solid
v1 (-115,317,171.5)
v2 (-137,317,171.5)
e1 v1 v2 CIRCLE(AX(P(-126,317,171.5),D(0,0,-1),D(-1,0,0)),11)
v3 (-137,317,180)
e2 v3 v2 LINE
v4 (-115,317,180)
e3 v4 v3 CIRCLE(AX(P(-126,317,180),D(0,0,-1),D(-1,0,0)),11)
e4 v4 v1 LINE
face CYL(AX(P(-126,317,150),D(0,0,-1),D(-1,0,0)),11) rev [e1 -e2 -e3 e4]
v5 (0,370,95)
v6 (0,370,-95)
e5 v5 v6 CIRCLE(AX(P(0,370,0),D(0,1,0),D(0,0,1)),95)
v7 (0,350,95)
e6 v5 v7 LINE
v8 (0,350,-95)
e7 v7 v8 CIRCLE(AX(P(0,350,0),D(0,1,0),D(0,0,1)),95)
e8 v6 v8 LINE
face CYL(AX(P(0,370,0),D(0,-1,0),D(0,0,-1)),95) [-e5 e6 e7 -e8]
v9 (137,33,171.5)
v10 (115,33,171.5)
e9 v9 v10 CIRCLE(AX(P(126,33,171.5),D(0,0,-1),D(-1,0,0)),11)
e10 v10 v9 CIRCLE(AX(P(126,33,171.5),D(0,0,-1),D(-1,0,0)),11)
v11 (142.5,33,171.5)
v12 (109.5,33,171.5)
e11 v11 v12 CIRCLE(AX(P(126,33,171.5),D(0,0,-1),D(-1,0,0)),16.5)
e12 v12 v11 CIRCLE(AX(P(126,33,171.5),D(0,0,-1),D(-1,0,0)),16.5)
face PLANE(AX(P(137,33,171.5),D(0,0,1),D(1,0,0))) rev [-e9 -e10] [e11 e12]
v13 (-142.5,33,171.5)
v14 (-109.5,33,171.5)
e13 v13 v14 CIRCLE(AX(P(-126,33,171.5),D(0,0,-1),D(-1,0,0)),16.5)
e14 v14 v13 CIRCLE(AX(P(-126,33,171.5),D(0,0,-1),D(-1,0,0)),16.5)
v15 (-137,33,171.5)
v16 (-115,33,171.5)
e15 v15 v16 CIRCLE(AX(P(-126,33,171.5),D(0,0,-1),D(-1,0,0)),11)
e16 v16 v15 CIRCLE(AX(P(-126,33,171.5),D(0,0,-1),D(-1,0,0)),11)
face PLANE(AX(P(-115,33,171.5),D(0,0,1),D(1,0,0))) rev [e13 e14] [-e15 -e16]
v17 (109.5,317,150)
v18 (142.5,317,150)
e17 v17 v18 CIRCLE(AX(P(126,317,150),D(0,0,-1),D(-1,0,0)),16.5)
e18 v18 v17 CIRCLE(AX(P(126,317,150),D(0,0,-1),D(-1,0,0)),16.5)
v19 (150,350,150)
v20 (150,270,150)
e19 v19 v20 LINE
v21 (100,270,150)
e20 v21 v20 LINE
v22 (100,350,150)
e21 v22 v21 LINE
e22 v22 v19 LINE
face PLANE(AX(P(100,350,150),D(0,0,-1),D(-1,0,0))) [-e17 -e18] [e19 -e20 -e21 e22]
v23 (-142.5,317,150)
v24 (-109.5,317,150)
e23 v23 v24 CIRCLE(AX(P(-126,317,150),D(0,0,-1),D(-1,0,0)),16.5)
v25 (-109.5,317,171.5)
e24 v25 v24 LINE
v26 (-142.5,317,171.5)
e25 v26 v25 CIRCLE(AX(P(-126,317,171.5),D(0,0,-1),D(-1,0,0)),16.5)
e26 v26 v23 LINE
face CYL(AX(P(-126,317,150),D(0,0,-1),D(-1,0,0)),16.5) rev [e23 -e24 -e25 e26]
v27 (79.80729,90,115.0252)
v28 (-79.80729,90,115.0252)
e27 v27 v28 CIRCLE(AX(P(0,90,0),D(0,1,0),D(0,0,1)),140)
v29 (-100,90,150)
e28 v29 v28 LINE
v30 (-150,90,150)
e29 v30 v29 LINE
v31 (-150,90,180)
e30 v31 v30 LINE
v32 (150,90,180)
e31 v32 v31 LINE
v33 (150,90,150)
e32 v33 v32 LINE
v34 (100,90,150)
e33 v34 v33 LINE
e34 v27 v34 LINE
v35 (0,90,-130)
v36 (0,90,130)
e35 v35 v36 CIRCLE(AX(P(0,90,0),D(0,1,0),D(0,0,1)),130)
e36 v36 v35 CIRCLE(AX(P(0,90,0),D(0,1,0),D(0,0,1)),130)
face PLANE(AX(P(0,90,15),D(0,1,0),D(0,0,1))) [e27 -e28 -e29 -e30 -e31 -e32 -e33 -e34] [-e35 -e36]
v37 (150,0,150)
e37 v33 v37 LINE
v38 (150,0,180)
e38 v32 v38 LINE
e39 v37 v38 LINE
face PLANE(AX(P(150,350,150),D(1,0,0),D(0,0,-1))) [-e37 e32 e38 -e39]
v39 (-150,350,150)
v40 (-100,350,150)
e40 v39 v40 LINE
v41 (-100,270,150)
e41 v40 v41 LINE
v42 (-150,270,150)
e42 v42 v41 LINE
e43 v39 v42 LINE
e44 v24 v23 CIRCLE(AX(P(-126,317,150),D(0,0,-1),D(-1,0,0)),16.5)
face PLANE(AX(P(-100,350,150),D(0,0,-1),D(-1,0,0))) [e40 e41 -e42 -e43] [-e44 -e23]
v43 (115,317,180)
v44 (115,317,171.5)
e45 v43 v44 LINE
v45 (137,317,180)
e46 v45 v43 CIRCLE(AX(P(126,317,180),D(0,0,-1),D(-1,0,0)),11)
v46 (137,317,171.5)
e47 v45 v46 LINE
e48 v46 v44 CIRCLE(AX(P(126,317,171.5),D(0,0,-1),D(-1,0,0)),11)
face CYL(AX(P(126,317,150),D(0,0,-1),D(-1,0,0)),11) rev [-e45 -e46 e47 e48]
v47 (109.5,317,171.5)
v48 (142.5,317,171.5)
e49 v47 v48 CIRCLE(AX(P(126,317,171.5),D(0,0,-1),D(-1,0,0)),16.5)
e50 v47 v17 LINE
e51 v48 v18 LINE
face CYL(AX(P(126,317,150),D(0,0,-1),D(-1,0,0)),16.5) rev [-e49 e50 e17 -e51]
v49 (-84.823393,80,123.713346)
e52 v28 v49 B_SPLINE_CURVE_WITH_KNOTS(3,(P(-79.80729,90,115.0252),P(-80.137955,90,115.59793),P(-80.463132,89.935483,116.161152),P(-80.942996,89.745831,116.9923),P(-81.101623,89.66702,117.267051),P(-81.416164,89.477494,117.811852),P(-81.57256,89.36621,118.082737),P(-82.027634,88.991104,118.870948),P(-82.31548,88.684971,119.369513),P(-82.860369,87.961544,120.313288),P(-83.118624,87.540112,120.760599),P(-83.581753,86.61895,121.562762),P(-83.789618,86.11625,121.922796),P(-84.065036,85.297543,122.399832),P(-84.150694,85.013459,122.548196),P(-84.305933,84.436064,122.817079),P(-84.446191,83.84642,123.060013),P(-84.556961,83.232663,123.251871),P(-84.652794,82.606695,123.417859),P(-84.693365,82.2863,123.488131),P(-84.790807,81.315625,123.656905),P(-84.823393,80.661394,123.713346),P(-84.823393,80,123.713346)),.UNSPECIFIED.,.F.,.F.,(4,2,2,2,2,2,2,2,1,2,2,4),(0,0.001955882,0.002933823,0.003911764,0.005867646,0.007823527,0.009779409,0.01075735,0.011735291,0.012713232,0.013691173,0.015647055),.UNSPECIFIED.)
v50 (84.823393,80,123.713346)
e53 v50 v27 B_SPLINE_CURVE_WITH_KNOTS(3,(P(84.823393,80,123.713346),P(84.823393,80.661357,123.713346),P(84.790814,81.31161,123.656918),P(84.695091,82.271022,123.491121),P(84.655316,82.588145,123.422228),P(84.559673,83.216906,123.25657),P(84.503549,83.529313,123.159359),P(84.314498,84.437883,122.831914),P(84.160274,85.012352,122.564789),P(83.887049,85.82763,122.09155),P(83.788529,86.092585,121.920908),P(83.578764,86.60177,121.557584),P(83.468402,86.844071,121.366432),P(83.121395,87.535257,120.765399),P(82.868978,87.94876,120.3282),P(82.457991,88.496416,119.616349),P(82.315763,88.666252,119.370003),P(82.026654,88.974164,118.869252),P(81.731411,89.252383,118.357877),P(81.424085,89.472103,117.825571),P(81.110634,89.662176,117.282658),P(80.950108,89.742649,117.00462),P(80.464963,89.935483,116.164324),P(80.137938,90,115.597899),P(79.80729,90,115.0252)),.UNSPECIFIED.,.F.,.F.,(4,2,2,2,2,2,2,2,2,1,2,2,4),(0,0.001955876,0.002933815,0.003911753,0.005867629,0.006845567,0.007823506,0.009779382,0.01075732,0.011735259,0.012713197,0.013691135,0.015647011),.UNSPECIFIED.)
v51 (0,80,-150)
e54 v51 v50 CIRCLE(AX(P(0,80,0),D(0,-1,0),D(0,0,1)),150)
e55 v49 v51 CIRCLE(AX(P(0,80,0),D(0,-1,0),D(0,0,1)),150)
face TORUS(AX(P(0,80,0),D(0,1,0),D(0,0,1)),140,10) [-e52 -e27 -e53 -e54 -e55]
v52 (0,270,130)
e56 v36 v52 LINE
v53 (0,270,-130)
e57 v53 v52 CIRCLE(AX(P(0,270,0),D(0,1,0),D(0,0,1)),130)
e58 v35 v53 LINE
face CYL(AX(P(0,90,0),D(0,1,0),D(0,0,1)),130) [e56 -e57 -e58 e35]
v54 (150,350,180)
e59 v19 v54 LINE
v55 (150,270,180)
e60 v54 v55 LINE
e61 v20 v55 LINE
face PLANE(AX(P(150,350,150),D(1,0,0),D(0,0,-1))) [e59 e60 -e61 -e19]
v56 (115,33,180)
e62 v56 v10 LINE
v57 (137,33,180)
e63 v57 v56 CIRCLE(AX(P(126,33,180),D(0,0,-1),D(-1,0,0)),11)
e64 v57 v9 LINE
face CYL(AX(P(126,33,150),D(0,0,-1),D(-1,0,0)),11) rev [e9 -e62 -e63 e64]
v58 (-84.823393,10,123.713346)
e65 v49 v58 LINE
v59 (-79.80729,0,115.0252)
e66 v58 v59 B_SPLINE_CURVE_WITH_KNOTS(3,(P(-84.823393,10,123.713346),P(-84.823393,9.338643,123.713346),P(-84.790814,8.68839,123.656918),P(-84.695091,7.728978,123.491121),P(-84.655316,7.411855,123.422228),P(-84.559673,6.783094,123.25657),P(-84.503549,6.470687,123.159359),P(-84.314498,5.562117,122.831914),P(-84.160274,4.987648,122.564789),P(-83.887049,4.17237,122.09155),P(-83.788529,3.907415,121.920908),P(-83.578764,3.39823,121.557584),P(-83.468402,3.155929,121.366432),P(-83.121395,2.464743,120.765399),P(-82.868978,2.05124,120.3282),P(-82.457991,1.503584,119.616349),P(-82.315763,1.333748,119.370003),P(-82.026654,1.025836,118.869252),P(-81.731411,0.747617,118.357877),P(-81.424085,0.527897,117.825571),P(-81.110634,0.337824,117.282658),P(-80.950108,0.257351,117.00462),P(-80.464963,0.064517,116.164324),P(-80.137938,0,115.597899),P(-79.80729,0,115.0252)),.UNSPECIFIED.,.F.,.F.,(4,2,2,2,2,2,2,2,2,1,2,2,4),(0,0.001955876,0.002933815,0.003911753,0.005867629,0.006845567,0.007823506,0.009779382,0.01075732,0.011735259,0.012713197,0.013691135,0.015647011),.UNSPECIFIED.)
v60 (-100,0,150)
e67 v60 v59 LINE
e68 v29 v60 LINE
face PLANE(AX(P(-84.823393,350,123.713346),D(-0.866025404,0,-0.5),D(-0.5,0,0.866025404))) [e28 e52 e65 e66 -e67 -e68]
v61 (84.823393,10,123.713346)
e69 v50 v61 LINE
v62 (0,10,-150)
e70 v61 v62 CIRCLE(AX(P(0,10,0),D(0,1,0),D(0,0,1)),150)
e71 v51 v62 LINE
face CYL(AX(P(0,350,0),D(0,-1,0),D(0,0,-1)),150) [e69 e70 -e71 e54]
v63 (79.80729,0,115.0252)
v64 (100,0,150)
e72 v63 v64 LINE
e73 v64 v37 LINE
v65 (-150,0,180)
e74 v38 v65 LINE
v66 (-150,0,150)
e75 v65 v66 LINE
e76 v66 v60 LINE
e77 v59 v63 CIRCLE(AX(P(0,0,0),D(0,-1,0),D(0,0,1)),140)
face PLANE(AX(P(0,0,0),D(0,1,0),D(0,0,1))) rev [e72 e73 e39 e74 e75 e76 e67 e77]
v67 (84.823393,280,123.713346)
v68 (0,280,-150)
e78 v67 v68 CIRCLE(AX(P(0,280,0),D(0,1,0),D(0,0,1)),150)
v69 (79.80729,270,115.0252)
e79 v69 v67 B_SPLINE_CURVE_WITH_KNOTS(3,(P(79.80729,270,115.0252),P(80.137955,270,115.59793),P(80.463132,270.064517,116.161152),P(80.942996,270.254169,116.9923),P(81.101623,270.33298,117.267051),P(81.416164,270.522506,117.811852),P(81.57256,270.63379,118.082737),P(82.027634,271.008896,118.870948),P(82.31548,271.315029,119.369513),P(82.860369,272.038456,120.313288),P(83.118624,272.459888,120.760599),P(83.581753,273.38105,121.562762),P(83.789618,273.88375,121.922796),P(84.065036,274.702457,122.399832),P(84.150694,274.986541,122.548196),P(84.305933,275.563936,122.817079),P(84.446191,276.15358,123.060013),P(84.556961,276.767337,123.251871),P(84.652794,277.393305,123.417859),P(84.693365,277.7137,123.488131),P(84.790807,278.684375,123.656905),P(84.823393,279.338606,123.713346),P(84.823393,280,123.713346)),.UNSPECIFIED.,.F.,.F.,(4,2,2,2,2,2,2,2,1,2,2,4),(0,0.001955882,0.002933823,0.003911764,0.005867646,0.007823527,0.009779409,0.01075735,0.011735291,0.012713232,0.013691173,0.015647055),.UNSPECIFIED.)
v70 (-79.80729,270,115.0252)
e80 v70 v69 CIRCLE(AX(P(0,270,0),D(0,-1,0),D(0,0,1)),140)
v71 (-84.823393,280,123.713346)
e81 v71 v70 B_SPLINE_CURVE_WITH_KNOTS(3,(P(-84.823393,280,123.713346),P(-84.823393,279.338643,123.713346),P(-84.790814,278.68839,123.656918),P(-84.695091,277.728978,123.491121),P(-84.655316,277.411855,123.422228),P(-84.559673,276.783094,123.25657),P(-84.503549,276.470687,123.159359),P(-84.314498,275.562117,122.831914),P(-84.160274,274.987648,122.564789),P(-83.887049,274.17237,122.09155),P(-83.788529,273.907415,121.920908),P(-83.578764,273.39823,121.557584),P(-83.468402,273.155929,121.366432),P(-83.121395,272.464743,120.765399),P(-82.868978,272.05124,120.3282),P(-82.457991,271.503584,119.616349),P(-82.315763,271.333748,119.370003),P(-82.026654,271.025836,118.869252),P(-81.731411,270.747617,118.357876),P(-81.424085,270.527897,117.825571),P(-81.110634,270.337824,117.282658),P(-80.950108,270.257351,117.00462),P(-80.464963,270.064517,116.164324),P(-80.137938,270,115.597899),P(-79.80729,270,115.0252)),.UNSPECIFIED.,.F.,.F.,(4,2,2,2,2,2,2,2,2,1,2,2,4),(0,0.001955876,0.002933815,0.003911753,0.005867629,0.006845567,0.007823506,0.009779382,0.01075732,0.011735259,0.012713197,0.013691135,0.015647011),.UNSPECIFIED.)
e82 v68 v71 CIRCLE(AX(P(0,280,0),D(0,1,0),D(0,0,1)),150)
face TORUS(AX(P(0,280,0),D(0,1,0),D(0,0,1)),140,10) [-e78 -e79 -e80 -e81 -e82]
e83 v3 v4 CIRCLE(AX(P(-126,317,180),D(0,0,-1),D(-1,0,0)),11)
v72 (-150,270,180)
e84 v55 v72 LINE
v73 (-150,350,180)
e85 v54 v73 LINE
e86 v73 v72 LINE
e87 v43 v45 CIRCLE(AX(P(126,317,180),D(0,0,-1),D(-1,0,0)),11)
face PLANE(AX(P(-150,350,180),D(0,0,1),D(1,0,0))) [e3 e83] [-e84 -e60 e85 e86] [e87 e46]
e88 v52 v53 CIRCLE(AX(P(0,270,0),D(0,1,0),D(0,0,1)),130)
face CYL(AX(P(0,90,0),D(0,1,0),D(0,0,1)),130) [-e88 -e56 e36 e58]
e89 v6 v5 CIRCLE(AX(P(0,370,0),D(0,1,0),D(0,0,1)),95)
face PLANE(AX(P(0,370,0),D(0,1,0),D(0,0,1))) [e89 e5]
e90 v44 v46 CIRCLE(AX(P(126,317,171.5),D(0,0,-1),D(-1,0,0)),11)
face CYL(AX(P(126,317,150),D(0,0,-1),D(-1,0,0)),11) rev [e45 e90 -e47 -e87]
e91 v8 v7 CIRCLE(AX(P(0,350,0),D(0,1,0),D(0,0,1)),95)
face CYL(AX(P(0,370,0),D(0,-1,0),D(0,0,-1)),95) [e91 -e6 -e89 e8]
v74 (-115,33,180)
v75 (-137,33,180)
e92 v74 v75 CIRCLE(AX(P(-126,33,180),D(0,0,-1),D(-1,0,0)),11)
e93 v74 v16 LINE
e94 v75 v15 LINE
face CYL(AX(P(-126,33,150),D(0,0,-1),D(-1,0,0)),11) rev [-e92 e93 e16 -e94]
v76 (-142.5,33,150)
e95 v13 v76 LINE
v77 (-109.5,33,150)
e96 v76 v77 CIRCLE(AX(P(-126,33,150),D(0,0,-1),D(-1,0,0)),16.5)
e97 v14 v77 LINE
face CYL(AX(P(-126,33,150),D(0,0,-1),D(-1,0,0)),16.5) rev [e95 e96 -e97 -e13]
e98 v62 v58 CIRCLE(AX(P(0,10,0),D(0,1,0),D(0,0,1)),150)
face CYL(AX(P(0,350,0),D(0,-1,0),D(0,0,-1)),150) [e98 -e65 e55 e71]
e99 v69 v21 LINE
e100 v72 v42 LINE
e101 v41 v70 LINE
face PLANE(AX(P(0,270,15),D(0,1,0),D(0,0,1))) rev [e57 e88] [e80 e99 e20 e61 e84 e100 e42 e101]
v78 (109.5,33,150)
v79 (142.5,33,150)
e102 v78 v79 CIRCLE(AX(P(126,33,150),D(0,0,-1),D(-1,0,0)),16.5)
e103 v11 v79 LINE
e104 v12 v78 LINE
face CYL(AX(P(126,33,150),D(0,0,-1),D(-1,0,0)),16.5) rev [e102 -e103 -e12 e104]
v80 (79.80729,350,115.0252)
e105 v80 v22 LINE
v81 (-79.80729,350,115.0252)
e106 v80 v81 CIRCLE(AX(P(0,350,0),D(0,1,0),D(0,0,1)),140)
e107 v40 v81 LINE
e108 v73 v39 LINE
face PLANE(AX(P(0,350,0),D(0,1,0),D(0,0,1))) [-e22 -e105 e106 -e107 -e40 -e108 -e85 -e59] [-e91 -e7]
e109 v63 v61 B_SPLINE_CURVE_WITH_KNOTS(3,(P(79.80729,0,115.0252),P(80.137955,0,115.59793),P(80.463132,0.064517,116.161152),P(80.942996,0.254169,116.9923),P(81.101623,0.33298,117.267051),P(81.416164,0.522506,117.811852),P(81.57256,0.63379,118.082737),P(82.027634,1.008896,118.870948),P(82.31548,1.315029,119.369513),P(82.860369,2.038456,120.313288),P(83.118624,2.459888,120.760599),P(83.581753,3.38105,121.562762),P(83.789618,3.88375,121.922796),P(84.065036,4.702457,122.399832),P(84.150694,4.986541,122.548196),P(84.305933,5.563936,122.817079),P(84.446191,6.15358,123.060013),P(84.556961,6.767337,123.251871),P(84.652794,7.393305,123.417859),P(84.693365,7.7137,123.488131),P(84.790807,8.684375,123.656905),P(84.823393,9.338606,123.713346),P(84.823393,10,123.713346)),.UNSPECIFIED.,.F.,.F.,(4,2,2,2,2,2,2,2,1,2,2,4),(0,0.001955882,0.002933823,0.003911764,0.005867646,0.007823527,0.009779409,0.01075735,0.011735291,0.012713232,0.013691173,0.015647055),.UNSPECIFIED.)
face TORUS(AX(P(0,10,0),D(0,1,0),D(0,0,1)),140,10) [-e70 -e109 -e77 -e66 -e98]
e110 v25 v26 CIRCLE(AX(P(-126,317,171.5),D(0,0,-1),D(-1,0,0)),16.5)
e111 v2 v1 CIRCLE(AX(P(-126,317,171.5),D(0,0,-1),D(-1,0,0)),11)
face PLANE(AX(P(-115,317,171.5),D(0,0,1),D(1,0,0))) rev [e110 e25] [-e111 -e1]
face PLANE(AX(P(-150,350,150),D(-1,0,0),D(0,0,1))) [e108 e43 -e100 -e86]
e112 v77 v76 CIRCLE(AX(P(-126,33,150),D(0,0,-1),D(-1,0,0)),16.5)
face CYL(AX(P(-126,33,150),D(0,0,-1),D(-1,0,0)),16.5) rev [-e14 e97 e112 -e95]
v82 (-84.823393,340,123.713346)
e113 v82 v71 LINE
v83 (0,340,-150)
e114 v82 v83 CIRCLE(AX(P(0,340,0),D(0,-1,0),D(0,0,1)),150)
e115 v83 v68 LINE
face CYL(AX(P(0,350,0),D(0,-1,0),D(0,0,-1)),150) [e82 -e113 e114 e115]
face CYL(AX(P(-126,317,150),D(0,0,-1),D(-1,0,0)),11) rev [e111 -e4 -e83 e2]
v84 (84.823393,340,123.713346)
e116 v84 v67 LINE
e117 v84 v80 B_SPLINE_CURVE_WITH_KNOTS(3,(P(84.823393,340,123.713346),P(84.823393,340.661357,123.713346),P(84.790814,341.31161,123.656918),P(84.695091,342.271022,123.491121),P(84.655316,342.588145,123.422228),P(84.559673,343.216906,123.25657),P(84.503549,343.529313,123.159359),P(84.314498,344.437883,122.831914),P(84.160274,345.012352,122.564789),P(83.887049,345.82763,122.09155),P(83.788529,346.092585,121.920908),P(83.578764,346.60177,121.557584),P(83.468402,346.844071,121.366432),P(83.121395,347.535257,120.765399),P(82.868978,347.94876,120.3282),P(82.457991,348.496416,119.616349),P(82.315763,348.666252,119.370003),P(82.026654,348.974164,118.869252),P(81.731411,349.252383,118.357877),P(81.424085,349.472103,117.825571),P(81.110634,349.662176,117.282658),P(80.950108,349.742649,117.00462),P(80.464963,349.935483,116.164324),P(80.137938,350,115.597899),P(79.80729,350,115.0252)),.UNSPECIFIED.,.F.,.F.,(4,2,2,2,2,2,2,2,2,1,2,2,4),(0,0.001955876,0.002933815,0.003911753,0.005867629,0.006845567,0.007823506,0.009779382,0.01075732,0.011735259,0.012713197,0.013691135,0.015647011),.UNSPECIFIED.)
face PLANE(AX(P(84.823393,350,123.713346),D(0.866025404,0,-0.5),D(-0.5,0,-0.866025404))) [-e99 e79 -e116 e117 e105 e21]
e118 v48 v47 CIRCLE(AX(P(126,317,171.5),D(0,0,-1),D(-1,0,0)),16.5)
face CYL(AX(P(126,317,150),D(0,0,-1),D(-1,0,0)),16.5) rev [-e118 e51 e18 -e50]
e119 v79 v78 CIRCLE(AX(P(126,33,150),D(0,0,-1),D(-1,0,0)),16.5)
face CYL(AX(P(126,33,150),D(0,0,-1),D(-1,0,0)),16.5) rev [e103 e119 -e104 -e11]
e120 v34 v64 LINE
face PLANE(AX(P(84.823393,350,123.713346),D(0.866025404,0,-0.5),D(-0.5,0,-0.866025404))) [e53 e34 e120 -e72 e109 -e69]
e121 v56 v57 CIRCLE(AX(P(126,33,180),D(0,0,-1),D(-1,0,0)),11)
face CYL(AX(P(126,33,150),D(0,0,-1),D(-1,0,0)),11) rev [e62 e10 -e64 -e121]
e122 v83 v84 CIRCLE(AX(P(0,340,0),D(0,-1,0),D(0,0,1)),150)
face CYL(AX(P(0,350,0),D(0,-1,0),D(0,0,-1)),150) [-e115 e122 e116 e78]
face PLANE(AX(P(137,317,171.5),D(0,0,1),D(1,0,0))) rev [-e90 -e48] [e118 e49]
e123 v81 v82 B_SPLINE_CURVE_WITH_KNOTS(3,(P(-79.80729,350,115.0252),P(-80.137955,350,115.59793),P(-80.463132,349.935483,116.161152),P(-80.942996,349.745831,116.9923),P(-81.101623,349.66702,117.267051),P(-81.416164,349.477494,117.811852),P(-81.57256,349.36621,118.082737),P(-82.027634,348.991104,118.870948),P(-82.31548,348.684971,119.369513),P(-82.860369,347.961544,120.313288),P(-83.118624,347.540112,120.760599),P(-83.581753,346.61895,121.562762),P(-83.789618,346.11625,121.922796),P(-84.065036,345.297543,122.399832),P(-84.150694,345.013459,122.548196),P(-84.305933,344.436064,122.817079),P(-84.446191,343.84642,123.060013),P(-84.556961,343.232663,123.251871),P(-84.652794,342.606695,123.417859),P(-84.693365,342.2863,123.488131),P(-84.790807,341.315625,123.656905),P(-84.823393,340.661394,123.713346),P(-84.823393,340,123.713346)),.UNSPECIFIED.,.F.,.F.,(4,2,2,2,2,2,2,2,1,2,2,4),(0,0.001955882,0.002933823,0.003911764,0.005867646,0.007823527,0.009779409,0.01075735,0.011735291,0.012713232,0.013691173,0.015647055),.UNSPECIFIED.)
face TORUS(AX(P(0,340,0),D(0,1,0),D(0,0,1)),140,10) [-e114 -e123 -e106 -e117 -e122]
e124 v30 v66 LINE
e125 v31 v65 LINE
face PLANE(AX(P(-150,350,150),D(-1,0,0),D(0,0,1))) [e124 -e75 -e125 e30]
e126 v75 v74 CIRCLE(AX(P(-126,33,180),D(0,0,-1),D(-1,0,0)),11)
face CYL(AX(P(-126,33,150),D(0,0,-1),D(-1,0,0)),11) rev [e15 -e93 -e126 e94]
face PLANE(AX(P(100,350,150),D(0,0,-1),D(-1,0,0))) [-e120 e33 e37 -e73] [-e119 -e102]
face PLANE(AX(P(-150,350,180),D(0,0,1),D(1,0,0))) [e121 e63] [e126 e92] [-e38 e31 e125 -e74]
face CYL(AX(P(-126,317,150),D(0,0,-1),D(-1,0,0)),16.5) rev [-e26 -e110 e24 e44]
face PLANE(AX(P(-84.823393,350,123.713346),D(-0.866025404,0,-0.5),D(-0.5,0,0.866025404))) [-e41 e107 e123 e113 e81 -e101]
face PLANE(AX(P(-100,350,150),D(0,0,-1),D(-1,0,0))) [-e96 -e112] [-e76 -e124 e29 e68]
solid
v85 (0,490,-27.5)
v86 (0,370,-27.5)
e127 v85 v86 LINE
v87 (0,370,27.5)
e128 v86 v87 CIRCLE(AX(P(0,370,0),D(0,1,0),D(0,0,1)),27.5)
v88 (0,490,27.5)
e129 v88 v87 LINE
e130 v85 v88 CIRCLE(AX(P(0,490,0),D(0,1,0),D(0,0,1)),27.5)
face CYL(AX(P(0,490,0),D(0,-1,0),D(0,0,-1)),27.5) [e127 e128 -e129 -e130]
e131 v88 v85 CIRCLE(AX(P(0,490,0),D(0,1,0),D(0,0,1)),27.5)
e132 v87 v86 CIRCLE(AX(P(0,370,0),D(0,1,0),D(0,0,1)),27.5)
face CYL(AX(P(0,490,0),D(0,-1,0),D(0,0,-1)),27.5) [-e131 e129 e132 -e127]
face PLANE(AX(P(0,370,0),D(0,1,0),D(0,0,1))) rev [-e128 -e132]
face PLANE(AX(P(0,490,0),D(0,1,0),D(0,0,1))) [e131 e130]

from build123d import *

# Parameters (mm, degrees)
SKETCH_1_R               = 150
EXTRUDE_1_DEPTH          = 350
EXTRUDE_2_DEPTH          = 350
SKETCH_3_R               = 95
EXTRUDE_3_DEPTH          = 20
CUT_EXTRUDE_START        = -80
SKETCH_4_OUTSIDE_W       = 417.896
SKETCH_4_OUTSIDE_H       = 447.896
SKETCH_4_OUTSIDE_R       = 130
CUT_EXTRUDE_1_DEPTH      = 180
FILLET_1_R               = 10
SKETCH_5_R               = 27.5
EXTRUDE_4_DEPTH          = 120
HOLE_WIZARD_1_AT_2_COUNT = 2
HOLE_WIZARD_1_AT_2_PITCH = 284
HOLE_WIZARD_1_AT_3_COUNT = 2
HOLE_WIZARD_1_AT_3_PITCH = 379.684079203
HOLE_WIZARD_1_AT_4_COUNT = 2
HOLE_WIZARD_1_AT_4_PITCH = 252


with BuildPart() as part:
    # 草图1 → 凸台-拉伸1 (new body)
    with BuildSketch(Plane(origin=(0, 0, 0), x_dir=(1, 0, 0), z_dir=(0, 1, 0))):
        with Locations(Location((0, 0, 0), (0, 0, 270))):
            Circle(SKETCH_1_R)
    extrude(amount=EXTRUDE_1_DEPTH)

    # 草图2 → 凸台-拉伸2 (add)
    with BuildSketch(Plane.XZ):
        with BuildLine():
            Line((-84.823393206, 123.713345946), (-100, 150))
            Line((-100, 150), (-150, 150))
            Line((-150, 150), (-150, 180))
            Line((-150, 180), (150, 180))
            Line((150, 180), (150, 150))
            Line((150, 150), (100, 150))
            Line((100, 150), (84.823393206, 123.713345946))
            ThreePointArc((84.823393206, 123.713345946), (0, 150), (-84.823393206, 123.713345946))
        make_face()
    extrude(amount=-EXTRUDE_2_DEPTH)

    # 草图3 → 凸台-拉伸3 (add)
    with BuildSketch(Plane(origin=(0, 350, 0), x_dir=(1, 0, 0), z_dir=(0, 1, 0))):
        with Locations(Location((0, 0, 0), (0, 0, 270))):
            Circle(SKETCH_3_R)
    extrude(amount=EXTRUDE_3_DEPTH)

    # 草图4 outside → 切除-拉伸1 (cut)
    with BuildSketch(Plane(origin=(0, 350, 0), x_dir=(1, 0, 0), z_dir=(0, 1, 0)).offset(CUT_EXTRUDE_START)):
        with Locations((0, -15)):
            Rectangle(SKETCH_4_OUTSIDE_W, SKETCH_4_OUTSIDE_H)
        with Locations(Location((0, 0, 0), (0, 0, 270))):
            Circle(SKETCH_4_OUTSIDE_R, mode=Mode.SUBTRACT)
    extrude(amount=-CUT_EXTRUDE_1_DEPTH, mode=Mode.SUBTRACT)

    # 圆角1
    fillet_1_edges = [part.edges().sort_by_distance(p)[0] for p in [
        (0, 0, -150),
        (0, 350, -150),
        (0, 270, -150),
        (0, 90, -150),
    ]]
    fillet(fillet_1_edges, radius=FILLET_1_R)

    # 草图7 → 打孔尺寸(%根据)内六角圆柱头螺钉的类型1 (revolve, cut)
    with BuildSketch(Plane(origin=(126, 317, 150), x_dir=(0, 1, 0), z_dir=(1, 0, 0))):
        Polygon((0, 0), (0, 30), (11, 30), (11, 21.5), (16.5, 21.5), (16.5, 0), align=None)
    hole_wizard_1 = revolve(axis=Axis((126, 317, 143.65), (0, 0, 1)), mode=Mode.SUBTRACT)

    # 打孔尺寸(%根据)内六角圆柱头螺钉的类型1 at 2: 打孔尺寸(%根据)内六角圆柱头螺钉的类型1 ×2
    with Locations(*[(0, -i * HOLE_WIZARD_1_AT_2_PITCH, 0) for i in range(1, HOLE_WIZARD_1_AT_2_COUNT)]):
        add(hole_wizard_1, mode=Mode.SUBTRACT)

    # 打孔尺寸(%根据)内六角圆柱头螺钉的类型1 at 3: 打孔尺寸(%根据)内六角圆柱头螺钉的类型1 ×2
    with Locations(*[Vector(-0.6637096834009412, -0.747990278118521, 0) * (i * HOLE_WIZARD_1_AT_3_PITCH) for i in range(1, HOLE_WIZARD_1_AT_3_COUNT)]):
        add(hole_wizard_1, mode=Mode.SUBTRACT)

    # 打孔尺寸(%根据)内六角圆柱头螺钉的类型1 at 4: 打孔尺寸(%根据)内六角圆柱头螺钉的类型1 ×2
    with Locations(*[(-i * HOLE_WIZARD_1_AT_4_PITCH, 0, 0) for i in range(1, HOLE_WIZARD_1_AT_4_COUNT)]):
        add(hole_wizard_1, mode=Mode.SUBTRACT)


with BuildPart() as body_2:
    # 草图5 → 凸台-拉伸4 (new body)
    with BuildSketch(Plane(origin=(0, 370, 0), x_dir=(1, 0, 0), z_dir=(0, 1, 0))):
        with Locations(Location((0, 0, 0), (0, 0, 90))):
            Circle(SKETCH_5_R)
    extrude(amount=EXTRUDE_4_DEPTH)


solid = Compound([part.part, body_2.part])
